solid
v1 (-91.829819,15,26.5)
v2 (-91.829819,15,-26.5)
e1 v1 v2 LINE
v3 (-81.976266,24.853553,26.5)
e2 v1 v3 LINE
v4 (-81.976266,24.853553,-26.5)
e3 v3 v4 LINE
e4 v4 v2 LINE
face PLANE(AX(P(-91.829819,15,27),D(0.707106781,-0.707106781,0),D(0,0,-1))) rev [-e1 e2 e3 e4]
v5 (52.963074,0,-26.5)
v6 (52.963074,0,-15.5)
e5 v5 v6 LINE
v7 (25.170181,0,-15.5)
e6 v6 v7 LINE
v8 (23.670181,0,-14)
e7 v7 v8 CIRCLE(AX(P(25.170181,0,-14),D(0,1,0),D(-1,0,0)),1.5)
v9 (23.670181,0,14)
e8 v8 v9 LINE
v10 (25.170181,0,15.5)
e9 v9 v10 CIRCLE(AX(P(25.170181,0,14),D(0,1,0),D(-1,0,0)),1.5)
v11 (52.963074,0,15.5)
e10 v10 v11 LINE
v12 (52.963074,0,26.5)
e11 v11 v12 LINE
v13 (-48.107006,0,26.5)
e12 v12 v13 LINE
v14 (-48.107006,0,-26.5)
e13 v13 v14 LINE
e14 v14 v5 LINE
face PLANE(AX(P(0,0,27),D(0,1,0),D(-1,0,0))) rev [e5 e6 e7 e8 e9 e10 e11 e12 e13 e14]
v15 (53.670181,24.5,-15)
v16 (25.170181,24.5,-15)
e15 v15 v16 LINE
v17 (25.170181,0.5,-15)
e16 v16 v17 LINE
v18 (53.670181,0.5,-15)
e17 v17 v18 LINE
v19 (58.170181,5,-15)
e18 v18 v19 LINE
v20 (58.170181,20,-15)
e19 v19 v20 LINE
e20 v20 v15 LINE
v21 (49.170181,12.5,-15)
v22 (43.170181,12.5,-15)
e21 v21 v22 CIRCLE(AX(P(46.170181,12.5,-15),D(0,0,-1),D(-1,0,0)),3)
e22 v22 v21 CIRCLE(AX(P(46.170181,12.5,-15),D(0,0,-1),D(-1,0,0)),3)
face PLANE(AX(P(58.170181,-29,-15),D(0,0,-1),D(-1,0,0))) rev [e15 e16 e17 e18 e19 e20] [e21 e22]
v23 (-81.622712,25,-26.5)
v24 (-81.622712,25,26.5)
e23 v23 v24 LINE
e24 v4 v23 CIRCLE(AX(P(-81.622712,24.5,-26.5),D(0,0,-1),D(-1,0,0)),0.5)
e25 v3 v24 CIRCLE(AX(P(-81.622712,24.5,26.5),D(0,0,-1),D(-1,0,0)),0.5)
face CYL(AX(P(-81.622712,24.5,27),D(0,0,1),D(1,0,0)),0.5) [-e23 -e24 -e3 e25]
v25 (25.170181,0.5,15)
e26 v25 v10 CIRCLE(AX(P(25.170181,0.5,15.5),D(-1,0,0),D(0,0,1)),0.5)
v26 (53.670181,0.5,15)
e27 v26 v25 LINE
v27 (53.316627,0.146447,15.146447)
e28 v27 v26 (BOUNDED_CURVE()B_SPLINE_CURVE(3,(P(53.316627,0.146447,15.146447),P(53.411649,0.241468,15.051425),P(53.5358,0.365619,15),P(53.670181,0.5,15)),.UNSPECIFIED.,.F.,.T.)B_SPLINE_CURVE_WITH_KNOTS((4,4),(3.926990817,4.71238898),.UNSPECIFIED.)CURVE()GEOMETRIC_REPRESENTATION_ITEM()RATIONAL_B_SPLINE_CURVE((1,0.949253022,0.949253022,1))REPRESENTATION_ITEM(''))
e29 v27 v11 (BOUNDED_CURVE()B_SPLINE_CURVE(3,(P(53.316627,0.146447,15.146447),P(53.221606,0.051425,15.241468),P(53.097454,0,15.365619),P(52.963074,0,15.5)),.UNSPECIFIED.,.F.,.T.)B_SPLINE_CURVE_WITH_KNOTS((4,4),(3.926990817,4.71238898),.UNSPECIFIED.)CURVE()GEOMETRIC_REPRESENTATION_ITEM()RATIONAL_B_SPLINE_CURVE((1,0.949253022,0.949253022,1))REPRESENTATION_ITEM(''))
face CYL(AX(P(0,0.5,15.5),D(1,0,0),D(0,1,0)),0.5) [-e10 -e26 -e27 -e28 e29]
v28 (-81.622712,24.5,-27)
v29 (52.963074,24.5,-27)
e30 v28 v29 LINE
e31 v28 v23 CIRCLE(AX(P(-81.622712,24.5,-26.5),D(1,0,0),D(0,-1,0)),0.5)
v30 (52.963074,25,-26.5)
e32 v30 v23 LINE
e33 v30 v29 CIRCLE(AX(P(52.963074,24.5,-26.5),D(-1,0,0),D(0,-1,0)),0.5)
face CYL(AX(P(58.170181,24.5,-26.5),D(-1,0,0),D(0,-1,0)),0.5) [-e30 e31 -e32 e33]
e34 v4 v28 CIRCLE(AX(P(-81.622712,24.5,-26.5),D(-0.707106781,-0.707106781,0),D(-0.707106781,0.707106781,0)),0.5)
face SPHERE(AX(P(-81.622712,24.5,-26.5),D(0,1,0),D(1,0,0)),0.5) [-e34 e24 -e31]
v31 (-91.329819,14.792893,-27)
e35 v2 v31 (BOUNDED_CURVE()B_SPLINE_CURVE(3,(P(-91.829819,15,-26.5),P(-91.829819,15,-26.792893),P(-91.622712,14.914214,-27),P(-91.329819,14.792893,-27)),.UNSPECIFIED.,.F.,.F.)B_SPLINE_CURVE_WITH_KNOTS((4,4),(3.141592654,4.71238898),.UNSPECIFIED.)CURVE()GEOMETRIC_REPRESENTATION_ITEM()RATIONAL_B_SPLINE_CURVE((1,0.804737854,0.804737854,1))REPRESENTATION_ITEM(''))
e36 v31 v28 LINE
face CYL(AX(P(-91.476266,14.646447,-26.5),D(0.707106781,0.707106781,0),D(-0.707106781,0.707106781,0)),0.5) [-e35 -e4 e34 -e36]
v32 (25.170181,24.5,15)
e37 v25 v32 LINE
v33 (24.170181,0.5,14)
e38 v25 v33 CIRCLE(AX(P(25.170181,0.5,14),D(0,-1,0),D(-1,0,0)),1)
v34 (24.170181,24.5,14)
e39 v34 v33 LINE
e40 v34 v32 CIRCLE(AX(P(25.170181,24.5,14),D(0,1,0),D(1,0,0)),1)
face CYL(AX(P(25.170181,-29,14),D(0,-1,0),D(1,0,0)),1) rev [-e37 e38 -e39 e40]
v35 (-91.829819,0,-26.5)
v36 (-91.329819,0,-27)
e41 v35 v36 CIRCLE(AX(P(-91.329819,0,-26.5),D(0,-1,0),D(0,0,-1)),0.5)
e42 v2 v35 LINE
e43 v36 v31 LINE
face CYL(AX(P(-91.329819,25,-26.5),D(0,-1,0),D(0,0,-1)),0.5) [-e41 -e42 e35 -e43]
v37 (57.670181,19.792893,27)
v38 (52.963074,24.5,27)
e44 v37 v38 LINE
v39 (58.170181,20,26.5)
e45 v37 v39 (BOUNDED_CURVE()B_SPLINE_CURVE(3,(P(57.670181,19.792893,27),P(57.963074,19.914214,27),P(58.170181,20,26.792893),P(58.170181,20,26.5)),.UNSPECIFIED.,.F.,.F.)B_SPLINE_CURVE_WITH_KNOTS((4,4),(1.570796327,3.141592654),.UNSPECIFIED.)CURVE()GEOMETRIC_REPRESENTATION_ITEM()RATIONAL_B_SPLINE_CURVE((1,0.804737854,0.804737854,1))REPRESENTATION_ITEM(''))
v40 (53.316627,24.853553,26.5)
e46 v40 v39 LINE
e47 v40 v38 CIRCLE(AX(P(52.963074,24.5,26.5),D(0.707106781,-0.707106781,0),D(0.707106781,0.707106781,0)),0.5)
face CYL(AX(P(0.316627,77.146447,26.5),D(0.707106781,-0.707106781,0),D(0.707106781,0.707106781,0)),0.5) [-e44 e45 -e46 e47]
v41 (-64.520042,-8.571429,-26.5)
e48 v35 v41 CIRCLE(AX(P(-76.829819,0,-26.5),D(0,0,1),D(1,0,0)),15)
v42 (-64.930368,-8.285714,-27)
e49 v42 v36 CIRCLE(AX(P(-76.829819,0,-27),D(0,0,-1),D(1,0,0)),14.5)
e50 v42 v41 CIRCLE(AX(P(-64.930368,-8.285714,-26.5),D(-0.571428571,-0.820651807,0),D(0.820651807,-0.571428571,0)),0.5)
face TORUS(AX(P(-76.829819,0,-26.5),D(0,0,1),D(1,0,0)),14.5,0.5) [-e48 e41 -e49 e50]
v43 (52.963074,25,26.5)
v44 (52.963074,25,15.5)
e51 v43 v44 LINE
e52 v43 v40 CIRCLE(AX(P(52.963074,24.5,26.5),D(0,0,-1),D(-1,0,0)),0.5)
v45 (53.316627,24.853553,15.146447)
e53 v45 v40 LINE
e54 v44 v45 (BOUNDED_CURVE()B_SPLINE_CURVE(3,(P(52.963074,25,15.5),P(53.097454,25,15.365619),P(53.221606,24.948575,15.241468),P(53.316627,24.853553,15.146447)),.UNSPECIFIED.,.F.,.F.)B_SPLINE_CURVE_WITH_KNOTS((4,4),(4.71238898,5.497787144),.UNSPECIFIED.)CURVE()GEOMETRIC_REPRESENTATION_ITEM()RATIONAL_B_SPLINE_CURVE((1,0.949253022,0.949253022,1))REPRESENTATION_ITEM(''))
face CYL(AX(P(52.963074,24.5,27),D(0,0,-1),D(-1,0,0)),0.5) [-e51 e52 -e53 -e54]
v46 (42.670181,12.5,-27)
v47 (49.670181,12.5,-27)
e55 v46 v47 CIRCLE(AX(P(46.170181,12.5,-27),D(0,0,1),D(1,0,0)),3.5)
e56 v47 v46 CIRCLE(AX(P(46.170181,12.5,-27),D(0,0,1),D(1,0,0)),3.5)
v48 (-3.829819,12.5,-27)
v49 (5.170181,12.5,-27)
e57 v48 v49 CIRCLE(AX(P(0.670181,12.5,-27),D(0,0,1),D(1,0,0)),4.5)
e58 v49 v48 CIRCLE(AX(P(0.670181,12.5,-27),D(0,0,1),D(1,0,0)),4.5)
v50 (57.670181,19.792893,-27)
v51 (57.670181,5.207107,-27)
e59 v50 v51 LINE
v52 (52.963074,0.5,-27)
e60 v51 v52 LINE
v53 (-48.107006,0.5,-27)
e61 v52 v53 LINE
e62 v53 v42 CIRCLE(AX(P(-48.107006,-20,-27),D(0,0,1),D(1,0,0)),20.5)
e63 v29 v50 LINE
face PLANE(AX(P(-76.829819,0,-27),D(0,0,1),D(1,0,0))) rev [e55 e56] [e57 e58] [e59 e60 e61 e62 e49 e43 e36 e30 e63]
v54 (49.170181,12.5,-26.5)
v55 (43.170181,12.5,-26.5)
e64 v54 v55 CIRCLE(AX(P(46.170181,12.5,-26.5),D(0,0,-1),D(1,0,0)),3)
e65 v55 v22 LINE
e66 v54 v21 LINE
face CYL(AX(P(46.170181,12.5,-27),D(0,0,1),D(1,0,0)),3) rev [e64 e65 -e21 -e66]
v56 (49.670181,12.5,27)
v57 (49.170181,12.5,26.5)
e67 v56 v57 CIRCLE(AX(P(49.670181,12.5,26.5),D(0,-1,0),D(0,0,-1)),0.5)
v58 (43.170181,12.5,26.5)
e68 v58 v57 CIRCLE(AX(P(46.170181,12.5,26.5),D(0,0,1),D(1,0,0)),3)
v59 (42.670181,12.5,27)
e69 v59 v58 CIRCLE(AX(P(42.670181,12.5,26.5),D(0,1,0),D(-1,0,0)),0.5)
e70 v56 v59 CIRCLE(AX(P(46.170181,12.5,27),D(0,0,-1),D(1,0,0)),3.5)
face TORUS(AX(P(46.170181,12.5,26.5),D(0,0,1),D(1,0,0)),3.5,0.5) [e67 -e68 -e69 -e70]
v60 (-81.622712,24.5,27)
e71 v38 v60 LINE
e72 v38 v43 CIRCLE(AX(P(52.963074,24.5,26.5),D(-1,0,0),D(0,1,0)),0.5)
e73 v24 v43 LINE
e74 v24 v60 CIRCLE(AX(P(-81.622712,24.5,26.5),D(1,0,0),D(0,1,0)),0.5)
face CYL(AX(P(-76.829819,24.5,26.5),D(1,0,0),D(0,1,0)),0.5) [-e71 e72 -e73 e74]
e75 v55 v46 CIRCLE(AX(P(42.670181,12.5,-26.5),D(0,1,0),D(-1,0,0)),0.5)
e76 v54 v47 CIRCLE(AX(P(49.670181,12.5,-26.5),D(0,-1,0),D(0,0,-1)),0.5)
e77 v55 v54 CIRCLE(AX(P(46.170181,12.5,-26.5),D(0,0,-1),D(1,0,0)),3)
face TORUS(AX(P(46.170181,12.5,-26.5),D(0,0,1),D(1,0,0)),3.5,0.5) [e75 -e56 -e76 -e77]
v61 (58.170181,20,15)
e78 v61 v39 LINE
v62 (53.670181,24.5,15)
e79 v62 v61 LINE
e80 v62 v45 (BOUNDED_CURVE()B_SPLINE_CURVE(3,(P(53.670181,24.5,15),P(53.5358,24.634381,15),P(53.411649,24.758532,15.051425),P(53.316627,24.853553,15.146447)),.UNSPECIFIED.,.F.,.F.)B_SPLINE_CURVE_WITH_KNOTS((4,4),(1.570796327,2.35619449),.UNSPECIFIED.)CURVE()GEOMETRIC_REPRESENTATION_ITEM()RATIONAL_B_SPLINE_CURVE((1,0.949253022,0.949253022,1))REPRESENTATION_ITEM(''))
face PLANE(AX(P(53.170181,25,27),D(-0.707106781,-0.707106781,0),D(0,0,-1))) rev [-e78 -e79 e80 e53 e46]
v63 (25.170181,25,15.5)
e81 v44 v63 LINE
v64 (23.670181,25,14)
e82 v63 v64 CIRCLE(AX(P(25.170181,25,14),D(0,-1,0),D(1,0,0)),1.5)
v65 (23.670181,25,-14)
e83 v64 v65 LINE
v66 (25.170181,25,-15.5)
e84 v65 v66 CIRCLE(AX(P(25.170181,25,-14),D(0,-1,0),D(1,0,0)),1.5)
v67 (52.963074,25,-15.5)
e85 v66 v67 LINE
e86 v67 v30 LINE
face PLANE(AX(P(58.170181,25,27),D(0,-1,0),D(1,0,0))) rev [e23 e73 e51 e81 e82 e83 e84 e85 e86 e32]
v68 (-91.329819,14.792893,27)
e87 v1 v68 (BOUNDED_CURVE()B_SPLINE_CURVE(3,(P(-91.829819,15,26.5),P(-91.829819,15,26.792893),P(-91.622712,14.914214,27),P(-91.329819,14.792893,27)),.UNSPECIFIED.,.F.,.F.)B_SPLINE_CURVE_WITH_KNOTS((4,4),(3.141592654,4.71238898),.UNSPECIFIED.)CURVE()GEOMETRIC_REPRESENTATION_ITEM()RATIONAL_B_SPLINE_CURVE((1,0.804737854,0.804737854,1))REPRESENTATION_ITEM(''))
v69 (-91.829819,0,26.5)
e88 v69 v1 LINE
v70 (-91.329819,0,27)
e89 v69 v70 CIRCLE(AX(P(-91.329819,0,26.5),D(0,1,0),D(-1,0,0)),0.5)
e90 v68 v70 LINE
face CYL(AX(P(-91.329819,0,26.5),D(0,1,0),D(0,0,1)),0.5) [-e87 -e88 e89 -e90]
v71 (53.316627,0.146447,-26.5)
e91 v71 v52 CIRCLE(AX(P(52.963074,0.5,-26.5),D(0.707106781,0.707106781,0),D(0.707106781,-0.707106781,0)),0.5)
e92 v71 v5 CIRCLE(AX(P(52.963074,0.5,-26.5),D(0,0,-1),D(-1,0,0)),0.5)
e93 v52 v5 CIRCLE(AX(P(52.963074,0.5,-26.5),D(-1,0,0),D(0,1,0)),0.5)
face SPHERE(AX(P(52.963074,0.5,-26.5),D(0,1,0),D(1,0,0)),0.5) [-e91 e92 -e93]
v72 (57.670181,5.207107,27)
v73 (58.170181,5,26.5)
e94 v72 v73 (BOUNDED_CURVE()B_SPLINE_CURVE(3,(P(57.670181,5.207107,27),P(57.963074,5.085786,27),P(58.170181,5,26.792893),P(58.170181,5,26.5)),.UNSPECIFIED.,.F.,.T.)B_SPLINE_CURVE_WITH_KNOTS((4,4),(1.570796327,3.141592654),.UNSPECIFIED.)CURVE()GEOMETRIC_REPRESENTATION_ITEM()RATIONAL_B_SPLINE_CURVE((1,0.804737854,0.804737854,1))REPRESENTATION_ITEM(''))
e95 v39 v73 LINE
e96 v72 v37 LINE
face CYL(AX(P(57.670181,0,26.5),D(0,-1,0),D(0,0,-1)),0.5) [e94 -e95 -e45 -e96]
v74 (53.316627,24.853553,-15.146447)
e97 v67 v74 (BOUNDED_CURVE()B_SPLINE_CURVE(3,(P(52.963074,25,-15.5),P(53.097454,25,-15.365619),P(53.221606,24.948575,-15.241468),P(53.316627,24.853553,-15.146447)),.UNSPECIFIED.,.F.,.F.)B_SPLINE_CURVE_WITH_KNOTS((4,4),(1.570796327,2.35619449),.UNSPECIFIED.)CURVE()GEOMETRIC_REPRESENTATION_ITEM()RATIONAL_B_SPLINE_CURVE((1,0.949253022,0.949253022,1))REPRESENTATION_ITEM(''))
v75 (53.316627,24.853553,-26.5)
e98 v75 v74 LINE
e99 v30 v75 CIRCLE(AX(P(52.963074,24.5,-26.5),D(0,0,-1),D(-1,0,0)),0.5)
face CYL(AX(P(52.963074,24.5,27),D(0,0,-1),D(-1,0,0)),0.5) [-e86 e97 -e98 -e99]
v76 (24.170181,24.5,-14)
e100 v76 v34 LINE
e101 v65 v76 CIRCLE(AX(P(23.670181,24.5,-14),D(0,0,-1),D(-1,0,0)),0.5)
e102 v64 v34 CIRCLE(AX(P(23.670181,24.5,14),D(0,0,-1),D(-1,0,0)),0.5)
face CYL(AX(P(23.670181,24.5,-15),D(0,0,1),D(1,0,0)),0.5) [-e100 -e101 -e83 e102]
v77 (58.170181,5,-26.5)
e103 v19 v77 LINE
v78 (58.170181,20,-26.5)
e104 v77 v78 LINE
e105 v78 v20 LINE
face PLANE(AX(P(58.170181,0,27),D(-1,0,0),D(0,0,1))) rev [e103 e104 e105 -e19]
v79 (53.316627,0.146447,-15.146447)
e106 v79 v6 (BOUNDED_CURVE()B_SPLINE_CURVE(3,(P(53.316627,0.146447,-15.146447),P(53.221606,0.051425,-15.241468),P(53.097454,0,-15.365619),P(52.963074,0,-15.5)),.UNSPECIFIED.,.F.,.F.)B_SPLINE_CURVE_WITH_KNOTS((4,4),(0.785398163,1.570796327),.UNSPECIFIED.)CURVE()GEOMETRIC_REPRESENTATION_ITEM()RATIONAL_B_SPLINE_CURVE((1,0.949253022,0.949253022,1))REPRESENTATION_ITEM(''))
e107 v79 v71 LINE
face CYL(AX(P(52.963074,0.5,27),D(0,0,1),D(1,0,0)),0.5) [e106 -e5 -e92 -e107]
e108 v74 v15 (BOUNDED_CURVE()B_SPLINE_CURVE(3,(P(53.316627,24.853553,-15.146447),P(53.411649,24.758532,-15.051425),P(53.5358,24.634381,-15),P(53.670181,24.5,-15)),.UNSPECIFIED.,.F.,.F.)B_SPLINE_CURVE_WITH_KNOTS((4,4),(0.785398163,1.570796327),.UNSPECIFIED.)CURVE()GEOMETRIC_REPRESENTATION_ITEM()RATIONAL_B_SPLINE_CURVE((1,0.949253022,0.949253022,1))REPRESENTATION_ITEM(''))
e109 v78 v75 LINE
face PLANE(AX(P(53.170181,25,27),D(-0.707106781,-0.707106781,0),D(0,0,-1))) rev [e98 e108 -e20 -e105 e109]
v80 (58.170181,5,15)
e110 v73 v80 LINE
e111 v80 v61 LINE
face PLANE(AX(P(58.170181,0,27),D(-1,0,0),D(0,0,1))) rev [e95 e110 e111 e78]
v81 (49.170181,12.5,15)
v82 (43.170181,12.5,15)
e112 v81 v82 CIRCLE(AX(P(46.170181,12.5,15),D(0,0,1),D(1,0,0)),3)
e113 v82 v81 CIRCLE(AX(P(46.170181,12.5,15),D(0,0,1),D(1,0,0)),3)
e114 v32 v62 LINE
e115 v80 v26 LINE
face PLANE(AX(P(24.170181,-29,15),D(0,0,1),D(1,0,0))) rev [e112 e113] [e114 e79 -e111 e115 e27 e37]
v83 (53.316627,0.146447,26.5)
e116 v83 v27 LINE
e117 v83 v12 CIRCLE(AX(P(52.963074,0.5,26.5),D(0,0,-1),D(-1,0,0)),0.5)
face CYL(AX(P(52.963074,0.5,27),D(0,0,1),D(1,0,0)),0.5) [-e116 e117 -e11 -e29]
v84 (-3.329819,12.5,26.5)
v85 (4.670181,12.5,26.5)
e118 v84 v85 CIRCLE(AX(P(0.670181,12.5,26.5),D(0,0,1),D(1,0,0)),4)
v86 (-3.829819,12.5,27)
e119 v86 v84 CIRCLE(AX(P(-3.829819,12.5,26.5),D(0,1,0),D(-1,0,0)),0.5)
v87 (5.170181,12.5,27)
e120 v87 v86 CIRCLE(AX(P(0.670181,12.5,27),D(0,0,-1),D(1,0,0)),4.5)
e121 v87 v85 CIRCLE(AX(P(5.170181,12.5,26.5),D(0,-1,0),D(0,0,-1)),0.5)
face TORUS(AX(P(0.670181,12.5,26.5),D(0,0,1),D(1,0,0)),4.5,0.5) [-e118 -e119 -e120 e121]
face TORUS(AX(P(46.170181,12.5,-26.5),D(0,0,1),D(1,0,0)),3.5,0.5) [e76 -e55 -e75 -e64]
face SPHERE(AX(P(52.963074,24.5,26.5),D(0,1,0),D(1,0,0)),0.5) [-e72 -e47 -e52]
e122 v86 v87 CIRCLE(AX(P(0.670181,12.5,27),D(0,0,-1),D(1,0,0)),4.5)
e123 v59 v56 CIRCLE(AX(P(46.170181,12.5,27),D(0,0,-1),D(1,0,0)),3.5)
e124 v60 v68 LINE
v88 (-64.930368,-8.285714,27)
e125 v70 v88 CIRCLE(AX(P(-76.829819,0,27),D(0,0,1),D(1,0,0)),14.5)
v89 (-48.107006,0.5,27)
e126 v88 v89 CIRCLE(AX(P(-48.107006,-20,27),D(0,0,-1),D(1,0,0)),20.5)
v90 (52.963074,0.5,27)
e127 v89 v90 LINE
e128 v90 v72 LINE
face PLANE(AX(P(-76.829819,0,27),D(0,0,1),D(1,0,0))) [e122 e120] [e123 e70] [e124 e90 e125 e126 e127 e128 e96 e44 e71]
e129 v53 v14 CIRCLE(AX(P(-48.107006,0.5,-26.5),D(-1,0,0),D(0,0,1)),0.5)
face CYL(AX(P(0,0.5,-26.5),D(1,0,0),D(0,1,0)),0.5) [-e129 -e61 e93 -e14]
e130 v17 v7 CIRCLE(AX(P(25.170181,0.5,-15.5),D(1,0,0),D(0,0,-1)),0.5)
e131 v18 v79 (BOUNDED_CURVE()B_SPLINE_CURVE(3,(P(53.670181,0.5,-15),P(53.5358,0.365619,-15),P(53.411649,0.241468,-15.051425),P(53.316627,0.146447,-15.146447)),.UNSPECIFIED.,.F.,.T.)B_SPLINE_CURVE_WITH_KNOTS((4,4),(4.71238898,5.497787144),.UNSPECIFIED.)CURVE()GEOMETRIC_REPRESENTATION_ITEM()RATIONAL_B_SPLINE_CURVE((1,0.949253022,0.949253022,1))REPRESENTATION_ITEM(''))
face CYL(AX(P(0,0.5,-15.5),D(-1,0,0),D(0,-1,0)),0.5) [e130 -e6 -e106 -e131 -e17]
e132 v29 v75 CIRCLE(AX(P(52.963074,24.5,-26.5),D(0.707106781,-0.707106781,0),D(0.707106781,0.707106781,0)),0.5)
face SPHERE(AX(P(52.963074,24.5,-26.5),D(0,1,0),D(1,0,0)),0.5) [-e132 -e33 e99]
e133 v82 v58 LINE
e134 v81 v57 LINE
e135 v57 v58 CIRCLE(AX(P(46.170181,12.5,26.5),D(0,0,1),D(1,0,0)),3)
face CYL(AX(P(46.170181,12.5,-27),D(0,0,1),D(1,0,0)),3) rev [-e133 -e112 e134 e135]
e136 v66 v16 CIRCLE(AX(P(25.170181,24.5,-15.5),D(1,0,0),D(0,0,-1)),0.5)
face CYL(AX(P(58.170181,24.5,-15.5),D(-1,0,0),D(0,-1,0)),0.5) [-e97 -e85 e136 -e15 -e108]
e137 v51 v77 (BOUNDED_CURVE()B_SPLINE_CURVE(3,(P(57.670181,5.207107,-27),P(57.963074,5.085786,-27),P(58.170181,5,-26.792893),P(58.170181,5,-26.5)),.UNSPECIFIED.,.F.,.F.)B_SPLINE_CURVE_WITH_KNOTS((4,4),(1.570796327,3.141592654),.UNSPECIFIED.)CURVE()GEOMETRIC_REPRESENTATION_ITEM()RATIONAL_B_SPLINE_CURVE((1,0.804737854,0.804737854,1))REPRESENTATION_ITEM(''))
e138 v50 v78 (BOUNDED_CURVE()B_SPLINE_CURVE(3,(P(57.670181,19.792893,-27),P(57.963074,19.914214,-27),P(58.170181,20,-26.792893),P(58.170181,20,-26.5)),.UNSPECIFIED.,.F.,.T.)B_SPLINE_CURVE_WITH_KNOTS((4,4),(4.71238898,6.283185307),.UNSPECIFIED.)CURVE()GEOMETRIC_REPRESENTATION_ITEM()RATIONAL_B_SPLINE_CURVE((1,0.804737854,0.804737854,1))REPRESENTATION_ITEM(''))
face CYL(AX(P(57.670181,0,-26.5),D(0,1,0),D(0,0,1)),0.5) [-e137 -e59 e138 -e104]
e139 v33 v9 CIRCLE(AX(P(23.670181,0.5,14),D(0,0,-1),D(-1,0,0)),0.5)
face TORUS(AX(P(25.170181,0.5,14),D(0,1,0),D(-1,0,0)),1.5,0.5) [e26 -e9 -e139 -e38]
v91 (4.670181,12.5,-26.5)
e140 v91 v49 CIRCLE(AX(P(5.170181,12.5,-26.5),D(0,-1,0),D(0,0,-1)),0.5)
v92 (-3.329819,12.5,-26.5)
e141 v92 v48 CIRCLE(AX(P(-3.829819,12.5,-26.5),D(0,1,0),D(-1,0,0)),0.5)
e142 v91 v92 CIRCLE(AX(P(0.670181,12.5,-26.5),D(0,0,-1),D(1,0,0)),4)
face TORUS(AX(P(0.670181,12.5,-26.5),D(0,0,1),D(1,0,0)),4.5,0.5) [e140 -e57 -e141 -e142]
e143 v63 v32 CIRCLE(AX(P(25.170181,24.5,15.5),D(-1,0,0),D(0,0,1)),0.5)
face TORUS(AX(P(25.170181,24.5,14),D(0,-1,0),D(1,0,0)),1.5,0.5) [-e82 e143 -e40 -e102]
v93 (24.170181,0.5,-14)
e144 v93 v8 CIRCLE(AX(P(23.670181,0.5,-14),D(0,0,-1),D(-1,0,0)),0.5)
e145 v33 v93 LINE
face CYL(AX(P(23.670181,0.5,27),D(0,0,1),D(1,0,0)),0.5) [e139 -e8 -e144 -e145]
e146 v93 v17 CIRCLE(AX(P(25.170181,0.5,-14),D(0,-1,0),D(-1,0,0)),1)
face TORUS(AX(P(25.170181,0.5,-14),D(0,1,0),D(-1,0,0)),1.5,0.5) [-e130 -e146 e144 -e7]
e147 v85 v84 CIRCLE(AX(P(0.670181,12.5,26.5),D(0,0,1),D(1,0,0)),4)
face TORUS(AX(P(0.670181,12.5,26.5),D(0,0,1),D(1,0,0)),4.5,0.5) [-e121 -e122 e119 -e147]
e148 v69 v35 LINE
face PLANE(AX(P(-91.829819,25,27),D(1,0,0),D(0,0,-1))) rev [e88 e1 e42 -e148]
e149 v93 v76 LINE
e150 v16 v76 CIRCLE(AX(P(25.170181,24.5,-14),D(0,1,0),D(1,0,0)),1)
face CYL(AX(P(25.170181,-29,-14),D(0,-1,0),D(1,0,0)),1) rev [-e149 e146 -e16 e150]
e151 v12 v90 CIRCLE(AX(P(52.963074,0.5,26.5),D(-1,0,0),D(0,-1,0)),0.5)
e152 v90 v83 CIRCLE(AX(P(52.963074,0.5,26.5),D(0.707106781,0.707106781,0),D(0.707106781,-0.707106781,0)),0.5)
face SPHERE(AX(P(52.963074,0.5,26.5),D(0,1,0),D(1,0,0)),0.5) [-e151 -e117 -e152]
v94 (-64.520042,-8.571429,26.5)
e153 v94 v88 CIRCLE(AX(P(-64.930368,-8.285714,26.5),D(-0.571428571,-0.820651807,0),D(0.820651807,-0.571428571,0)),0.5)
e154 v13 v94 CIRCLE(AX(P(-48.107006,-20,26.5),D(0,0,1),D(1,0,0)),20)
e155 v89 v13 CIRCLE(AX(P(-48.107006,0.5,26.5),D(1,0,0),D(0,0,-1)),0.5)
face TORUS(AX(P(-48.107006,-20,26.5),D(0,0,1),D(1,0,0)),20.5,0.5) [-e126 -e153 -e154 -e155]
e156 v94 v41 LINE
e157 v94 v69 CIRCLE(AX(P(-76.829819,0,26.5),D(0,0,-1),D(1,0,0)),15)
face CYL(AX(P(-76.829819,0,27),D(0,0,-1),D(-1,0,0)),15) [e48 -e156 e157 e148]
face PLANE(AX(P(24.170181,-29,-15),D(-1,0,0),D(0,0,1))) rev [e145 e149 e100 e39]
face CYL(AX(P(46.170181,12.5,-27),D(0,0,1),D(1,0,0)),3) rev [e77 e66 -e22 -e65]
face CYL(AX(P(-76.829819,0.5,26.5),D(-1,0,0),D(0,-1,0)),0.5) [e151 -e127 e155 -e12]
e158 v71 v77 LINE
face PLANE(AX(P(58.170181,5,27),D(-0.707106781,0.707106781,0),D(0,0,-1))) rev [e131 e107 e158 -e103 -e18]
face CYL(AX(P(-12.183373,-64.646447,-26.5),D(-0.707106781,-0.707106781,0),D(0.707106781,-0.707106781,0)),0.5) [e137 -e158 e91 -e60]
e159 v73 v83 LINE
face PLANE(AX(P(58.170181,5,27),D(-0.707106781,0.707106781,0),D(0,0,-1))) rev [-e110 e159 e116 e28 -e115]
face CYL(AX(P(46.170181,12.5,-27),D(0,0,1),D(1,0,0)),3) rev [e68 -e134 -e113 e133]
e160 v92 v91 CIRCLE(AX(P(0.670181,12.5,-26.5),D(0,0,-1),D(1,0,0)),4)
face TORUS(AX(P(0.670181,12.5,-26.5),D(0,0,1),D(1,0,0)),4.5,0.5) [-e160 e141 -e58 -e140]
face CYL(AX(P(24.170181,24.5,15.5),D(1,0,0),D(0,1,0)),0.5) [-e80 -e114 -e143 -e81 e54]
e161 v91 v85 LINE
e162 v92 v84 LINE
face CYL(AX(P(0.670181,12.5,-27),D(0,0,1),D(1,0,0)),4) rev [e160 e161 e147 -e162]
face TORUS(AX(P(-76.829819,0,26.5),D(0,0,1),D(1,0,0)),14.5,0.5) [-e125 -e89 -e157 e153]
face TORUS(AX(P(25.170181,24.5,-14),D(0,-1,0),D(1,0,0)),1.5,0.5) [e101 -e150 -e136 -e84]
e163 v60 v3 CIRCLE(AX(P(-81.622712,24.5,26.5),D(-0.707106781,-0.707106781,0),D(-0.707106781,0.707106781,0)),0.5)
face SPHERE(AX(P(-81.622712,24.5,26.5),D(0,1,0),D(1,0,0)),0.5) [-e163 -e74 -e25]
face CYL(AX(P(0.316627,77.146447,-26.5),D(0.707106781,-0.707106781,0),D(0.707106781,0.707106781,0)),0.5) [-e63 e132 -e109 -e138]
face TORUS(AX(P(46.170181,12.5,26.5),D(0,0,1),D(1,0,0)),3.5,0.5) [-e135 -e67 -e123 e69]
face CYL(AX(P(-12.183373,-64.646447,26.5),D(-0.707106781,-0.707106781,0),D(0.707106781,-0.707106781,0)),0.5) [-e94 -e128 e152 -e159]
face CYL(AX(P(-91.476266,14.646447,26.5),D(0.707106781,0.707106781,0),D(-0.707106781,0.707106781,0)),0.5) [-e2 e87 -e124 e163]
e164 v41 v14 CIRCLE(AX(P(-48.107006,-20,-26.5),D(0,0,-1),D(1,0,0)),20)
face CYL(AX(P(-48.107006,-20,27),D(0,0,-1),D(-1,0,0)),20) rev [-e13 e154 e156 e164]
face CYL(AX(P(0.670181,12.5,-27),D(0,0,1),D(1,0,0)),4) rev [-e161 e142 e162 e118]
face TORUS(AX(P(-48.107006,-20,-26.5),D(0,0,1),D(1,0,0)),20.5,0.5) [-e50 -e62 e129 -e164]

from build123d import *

# Parameters (mm, degrees)
ARM_BODY_54MM_DEPTH      = 27
FORK_SLOT_SKETCH_W       = 34
FORK_SLOT_SKETCH_H       = 30
FORK_SLOT_12MM_DEPTH     = 54
END_CHAMFER_5MM_SIZE     = 5
CORNER_CHAMFER_10MM_SIZE = 10
PIN_HOLES_SKETCH_R       = 4
PIN_HOLES_SKETCH_R_2     = 3
PIN_HOLES_DEPTH          = 54
SLOT_FILLET_R1_R         = 1
EDGE_FILLET_R0_5_A_R     = 0.5
EDGE_FILLET_R0_5_B_R     = 0.5


with BuildPart() as part:
    # Arm Profile Sketch → Arm Body 54mm (new, symmetric)
    with BuildSketch(Plane.XY):
        with BuildLine():
            Line((0, 0), (-48.107006044, 0))
            ThreePointArc((-48.107006044, 0), (-57.365207042, -2.271894791), (-64.520042177, -8.571428571))
            ThreePointArc((-64.520042177, -8.571428571), (-81.321664305, -14.311650088), (-91.829819277, 0))
            Line((-91.829819277, 0), (-91.829819277, 25))
            Line((-91.829819277, 25), (58.170180723, 25))
            Line((58.170180723, 25), (58.170180723, 0))
            Line((58.170180723, 0), (0, 0))
        make_face()
    extrude(amount=ARM_BODY_54MM_DEPTH, both=True)

    # Fork Slot Sketch → Fork Slot 12mm (cut)
    with BuildSketch(Plane(origin=(0, 25, 0), x_dir=(1, 0, 0), z_dir=(0, 1, 0))):
        with Locations((41.170180723, 0)):
            Rectangle(FORK_SLOT_SKETCH_W, FORK_SLOT_SKETCH_H)
    extrude(amount=-FORK_SLOT_12MM_DEPTH, mode=Mode.SUBTRACT)

    # End Chamfer 5mm
    end_chamfer_5mm_edges = [part.edges().sort_by_distance(p)[0] for p in [
        (58.170180723, 25, 21),
        (58.170180723, 0, 21),
        (58.170180723, 0, -21),
        (58.170180723, 25, -21),
    ]]
    chamfer(end_chamfer_5mm_edges, length=END_CHAMFER_5MM_SIZE)

    # Corner Chamfer 10mm
    corner_chamfer_10mm_edges = [part.edges().sort_by_distance(p)[0] for p in [
        (-91.829819277, 25, 0),
    ]]
    chamfer(corner_chamfer_10mm_edges, length=CORNER_CHAMFER_10MM_SIZE)

    # Pin Holes Sketch → Pin Holes (cut)
    with BuildSketch(Plane.XY.offset(27)):
        with Locations((0.670180723, 12.5)):
            Circle(PIN_HOLES_SKETCH_R)
        with Locations((46.170180723, 12.5)):
            Circle(PIN_HOLES_SKETCH_R_2)
    extrude(amount=-PIN_HOLES_DEPTH, mode=Mode.SUBTRACT)

    # Slot Fillet R1
    slot_fillet_r1_edges = [part.edges().sort_by_distance(p)[0] for p in [
        (24.170180723, 12.5, 15),
        (24.170180723, 12.5, -15),
    ]]
    fillet(slot_fillet_r1_edges, radius=SLOT_FILLET_R1_R)

    # Edge Fillet R0.5 A
    edge_fillet_r0_5_a_edges = [part.edges().sort_by_distance(p)[0] for p in [
        (-81.321664305, -14.311650088, 27),
        (-57.365207042, -2.271894791, 27),
        (58.170180723, 12.5, -27),
        (-14.329819277, 25, -27),
        (55.670180723, 22.5, -27),
        (55.670180723, 2.5, -27),
        (2.531587339, 0, 27),
        (58.170180723, 12.5, 27),
        (-14.329819277, 25, 27),
        (55.670180723, 22.5, 27),
        (55.670180723, 2.5, 27),
        (-91.829819277, 7.5, -27),
        (-91.829819277, 7.5, 27),
        (-86.829819277, 20, -27),
        (-86.829819277, 20, 27),
        (2.531587339, 0, -27),
        (-57.365207042, -2.271894791, -27),
        (-3.329819277, 12.5, -27),
        (-3.329819277, 12.5, 27),
        (43.170180723, 12.5, -27),
        (43.170180723, 12.5, 27),
        (-81.321664305, -14.311650088, -27),
    ]]
    fillet(edge_fillet_r0_5_a_edges, radius=EDGE_FILLET_R0_5_A_R)

    # Edge Fillet R0.5 B
    edge_fillet_r0_5_b_edges = [part.edges().sort_by_distance(p)[0] for p in [
        (53.170180723, 25, 20.75),
        (53.170180723, 0, -20.75),
        (-81.829819277, 25, 0),
        (53.106600299, 0.153496722, 26.860465641),
        (-81.766238853, 24.846503278, 26.860465641),
        (53.106600299, 24.846503278, 26.860465641),
        (53.106600299, 24.846503278, -26.860465641),
        (-81.766238853, 24.846503278, -26.860465641),
        (53.106600299, 0.153496722, -26.860465641),
        (39.170180723, 0, -15),
        (53.170180723, 0, 20.75),
        (39.170180723, 25, -15),
        (53.170180723, 25, -20.75),
        (24.170180723, 25, 0),
        (24.170180723, 0, 0),
        (39.170180723, 0, 15),
        (39.170180723, 25, 15),
        (24.463073942, 25, -14.707106781),
        (24.463073942, 0, -14.707106781),
        (24.463073942, 25, 14.707106781),
        (24.463073942, 0, 14.707106781),
    ]]
    fillet(edge_fillet_r0_5_b_edges, radius=EDGE_FILLET_R0_5_B_R)


solid = part.part
